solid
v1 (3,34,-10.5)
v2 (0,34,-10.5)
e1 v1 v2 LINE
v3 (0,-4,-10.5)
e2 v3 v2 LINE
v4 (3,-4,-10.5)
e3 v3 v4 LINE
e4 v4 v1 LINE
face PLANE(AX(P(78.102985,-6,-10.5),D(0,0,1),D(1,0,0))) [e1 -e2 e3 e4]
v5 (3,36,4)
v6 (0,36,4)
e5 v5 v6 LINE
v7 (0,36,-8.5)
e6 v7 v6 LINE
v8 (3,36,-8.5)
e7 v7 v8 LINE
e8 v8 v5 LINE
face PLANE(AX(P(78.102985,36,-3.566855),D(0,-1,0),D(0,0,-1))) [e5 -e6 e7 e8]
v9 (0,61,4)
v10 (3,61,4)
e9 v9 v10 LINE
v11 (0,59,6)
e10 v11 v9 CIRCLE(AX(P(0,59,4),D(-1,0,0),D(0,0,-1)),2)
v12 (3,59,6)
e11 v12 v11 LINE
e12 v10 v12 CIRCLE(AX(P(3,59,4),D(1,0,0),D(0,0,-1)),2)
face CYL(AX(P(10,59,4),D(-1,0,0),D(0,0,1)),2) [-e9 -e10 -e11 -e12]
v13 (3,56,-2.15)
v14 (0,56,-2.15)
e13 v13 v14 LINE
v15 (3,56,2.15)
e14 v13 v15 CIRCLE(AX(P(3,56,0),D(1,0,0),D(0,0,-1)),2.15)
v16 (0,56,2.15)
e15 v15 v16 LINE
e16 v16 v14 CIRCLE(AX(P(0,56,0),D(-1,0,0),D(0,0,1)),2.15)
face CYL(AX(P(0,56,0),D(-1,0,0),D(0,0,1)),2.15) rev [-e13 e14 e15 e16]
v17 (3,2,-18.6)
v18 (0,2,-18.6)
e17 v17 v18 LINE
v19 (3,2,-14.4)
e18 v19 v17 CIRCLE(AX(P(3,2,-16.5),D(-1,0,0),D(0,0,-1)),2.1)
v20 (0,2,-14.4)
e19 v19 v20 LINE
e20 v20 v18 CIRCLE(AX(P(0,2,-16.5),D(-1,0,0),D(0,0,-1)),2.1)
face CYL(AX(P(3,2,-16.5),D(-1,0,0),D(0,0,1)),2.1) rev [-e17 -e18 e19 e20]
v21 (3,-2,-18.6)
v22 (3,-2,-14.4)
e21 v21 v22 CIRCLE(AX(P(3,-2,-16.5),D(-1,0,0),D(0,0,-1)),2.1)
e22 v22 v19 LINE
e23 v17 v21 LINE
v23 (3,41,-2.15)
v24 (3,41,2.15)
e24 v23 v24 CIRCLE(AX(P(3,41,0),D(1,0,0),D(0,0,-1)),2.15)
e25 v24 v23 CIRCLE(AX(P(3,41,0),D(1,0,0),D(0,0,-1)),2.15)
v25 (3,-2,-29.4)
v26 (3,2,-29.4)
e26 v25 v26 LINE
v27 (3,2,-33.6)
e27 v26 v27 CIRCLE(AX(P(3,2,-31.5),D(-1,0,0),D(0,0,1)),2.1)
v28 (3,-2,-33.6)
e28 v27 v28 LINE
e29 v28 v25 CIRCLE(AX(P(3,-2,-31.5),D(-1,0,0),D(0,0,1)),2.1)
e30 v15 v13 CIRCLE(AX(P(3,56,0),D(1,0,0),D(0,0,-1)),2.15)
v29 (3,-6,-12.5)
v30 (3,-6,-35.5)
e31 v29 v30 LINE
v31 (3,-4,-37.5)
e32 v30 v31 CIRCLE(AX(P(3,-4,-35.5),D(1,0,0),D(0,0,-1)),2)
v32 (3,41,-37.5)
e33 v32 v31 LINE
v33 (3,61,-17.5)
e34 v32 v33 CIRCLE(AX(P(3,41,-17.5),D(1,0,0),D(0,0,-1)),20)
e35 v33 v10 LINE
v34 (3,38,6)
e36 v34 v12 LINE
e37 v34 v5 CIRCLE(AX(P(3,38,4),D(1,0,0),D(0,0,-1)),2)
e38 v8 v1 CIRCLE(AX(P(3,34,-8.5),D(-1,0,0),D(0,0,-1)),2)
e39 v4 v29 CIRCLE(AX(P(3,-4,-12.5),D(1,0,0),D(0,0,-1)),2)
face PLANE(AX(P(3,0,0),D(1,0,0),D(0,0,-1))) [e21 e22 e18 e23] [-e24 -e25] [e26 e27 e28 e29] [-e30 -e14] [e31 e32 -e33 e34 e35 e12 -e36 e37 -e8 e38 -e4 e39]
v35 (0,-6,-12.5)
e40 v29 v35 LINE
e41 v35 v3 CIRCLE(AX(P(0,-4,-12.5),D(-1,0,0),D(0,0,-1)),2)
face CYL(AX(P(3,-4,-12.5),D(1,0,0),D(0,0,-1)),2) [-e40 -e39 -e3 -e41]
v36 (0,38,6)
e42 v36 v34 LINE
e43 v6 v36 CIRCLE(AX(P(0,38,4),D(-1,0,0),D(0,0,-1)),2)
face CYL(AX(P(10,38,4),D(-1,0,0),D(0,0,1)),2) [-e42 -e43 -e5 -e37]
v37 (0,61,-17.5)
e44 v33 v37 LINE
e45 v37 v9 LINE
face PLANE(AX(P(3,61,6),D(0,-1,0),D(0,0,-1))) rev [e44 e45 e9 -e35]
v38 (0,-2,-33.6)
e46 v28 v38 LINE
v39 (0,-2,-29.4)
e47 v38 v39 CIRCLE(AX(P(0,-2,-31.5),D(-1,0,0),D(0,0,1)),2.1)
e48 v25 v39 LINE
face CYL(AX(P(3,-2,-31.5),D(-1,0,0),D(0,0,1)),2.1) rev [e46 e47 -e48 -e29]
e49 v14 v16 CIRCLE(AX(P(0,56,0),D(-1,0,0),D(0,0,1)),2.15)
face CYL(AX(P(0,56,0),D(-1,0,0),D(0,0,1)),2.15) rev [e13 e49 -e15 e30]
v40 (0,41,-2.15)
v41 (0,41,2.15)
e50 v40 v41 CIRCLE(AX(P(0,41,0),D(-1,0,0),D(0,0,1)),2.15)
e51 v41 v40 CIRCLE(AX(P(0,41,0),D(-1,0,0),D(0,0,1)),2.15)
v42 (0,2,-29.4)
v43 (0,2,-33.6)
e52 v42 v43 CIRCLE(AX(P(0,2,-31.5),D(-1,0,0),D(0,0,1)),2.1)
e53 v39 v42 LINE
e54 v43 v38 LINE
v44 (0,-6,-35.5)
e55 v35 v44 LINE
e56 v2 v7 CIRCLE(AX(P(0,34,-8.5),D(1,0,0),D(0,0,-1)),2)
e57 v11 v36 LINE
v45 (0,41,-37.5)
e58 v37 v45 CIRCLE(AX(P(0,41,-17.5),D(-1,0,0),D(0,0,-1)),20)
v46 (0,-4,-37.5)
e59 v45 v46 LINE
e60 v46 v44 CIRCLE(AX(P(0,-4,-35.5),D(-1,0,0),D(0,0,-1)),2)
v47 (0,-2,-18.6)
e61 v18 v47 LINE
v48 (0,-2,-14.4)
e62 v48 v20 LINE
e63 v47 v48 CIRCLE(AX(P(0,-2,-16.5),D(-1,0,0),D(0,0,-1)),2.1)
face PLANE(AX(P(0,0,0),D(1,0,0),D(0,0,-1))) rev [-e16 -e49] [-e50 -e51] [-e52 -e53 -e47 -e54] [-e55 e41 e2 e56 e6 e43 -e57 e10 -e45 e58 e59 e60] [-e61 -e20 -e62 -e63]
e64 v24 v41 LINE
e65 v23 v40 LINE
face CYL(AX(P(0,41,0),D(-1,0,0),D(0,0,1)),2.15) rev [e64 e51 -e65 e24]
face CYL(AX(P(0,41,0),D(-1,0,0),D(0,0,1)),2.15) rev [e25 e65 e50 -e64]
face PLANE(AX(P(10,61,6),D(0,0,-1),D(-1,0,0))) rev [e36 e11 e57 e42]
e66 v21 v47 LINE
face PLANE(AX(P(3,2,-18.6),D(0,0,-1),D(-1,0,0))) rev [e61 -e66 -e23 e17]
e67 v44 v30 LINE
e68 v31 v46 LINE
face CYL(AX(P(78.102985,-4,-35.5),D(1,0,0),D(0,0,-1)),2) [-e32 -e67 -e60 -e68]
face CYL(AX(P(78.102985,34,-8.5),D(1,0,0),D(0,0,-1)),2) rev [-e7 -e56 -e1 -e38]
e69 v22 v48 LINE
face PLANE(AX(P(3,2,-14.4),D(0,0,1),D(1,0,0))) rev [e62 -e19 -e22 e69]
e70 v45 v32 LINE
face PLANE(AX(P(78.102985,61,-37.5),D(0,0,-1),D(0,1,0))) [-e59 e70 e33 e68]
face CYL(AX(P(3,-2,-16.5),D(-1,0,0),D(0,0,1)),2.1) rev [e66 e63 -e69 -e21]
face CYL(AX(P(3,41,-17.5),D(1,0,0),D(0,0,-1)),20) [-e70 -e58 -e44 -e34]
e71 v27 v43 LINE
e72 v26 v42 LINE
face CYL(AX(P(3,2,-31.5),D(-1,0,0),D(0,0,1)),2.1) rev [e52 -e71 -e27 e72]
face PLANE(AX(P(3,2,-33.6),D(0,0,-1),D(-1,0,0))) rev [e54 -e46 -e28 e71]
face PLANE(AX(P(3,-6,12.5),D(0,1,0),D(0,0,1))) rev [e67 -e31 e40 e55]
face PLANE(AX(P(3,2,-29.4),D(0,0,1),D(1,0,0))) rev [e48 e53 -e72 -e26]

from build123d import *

# Parameters (mm, degrees)
EXTRUDE_1_DEPTH             = 3
EXTRUDE_2_DEPTH             = 3
CUT_EXTRUDE_1_DEPTH         = 3
FILLET_2_R                  = 2
HOLE_WIZARD_4_3_4_3_1_D     = 4.3
HOLE_WIZARD_4_3_4_3_1_DEPTH = 10.1
HOLE_WIZARD_4_3_4_3_1_TIP   = 1.291850331
EXTRUDE_3_DEPTH             = 3
PATTERN_LINEAR_1_COUNT      = 2
PATTERN_LINEAR_1_PITCH      = 24
SKETCH_8_W                  = 24.221203915
SKETCH_8_H                  = 43.975746473
CUT_EXTRUDE_2_DEPTH         = 10
SKETCH_9_W                  = 8.594531195
SKETCH_9_H                  = 29.155429328
CUT_EXTRUDE_3_DEPTH         = 10
FILLET_3_R                  = 2
FILLET_4_R                  = 20


with BuildPart() as part:
    # 草图1 → 凸台-拉伸1 (new body)
    with BuildSketch(Plane(origin=(0, 0, 0), x_dir=(0, 0, -1), z_dir=(1, 0, 0))):
        Polygon((-12.5, 6), (-6, 6), (-6, 61), (6, 61), (6, 6), (12.5, 6), (12.5, -6), (-12.5, -6), align=None)
    extrude(amount=EXTRUDE_1_DEPTH)

    # 草图2 → 凸台-拉伸2 (add)
    with BuildSketch(Plane.ZY):
        Polygon((-6, 61), (-12.5, 6), (12.5, 6), (6, 61), align=None)
    extrude(amount=-EXTRUDE_2_DEPTH)

    # 草图3 → 切除-拉伸1 (cut)
    with BuildSketch(Plane.ZY):
        with BuildLine():
            Line((-5.4, 2), (-5.4, -2))
            ThreePointArc((-5.4, -2), (-7.5, -4.1), (-9.6, -2))
            Line((-9.6, -2), (-9.6, 2))
            ThreePointArc((-9.6, 2), (-7.5, 4.1), (-5.4, 2))
        make_face()
        with BuildLine():
            Line((5.4, 2), (5.4, -2))
            ThreePointArc((5.4, -2), (7.5, -4.1), (9.6, -2))
            Line((9.6, -2), (9.6, 2))
            ThreePointArc((9.6, 2), (7.5, 4.1), (5.4, 2))
        make_face()
    cut_extrude_1 = extrude(amount=-CUT_EXTRUDE_1_DEPTH, mode=Mode.SUBTRACT)

    # 圆角2
    fillet_2_edges = [part.edges().sort_by_distance(p)[0] for p in [
        (1.5, -6, -12.5),
        (1.5, -6, 12.5),
    ]]
    fillet(fillet_2_edges, radius=FILLET_2_R)

    # Ø4.3 (4.3) 直径孔1
    with Locations(Plane.ZY):
        with Locations((0, 56), (0, 41)):
            Hole(HOLE_WIZARD_4_3_4_3_1_D / 2, depth=HOLE_WIZARD_4_3_4_3_1_DEPTH)
            with Locations((0, 0, -(HOLE_WIZARD_4_3_4_3_1_DEPTH + HOLE_WIZARD_4_3_4_3_1_TIP / 2))):  # 118° drill point
                Cone(0, HOLE_WIZARD_4_3_4_3_1_D / 2, HOLE_WIZARD_4_3_4_3_1_TIP, mode=Mode.SUBTRACT)

    # 草图7 → 凸台-拉伸3 (add)
    with BuildSketch(Plane.ZY):
        Polygon((-3.566854944, 61), (-37.5, 61), (-37.5, -6), (-10.5, -6), (-10.5, 36), (-3.566854944, 36), align=None)
    extrude(amount=-EXTRUDE_3_DEPTH)

    # 阵列(线性)1: 切除-拉伸1 ×2
    with Locations(*[(0, 0, -i * PATTERN_LINEAR_1_PITCH) for i in range(1, PATTERN_LINEAR_1_COUNT)]):
        add(cut_extrude_1, mode=Mode.SUBTRACT)

    # 草图8 → 切除-拉伸2 (cut)
    with BuildSketch(Plane.ZY):
        with Locations((1.610601958, 14.012126763)):
            Rectangle(SKETCH_8_W, SKETCH_8_H)
    extrude(amount=-CUT_EXTRUDE_2_DEPTH, mode=Mode.SUBTRACT)

    # 草图9 → 切除-拉伸3 (cut)
    with BuildSketch(Plane.ZY):
        with Locations((10.297265598, 46.422285336)):
            Rectangle(SKETCH_9_W, SKETCH_9_H)
    extrude(amount=-CUT_EXTRUDE_3_DEPTH, mode=Mode.SUBTRACT)

    # 圆角3
    fillet_3_edges = [part.edges().sort_by_distance(p)[0] for p in [
        (1.5, -6, -37.5),
        (1.5, 36, -10.5),
        (1.5, 61, 6),
        (1.5, -6, -10.5),
        (1.5, 36, 6),
    ]]
    fillet(fillet_3_edges, radius=FILLET_3_R)

    # 圆角4
    fillet_4_edges = [part.edges().sort_by_distance(p)[0] for p in [
        (1.5, 61, -37.5),
    ]]
    fillet(fillet_4_edges, radius=FILLET_4_R)


solid = part.part
